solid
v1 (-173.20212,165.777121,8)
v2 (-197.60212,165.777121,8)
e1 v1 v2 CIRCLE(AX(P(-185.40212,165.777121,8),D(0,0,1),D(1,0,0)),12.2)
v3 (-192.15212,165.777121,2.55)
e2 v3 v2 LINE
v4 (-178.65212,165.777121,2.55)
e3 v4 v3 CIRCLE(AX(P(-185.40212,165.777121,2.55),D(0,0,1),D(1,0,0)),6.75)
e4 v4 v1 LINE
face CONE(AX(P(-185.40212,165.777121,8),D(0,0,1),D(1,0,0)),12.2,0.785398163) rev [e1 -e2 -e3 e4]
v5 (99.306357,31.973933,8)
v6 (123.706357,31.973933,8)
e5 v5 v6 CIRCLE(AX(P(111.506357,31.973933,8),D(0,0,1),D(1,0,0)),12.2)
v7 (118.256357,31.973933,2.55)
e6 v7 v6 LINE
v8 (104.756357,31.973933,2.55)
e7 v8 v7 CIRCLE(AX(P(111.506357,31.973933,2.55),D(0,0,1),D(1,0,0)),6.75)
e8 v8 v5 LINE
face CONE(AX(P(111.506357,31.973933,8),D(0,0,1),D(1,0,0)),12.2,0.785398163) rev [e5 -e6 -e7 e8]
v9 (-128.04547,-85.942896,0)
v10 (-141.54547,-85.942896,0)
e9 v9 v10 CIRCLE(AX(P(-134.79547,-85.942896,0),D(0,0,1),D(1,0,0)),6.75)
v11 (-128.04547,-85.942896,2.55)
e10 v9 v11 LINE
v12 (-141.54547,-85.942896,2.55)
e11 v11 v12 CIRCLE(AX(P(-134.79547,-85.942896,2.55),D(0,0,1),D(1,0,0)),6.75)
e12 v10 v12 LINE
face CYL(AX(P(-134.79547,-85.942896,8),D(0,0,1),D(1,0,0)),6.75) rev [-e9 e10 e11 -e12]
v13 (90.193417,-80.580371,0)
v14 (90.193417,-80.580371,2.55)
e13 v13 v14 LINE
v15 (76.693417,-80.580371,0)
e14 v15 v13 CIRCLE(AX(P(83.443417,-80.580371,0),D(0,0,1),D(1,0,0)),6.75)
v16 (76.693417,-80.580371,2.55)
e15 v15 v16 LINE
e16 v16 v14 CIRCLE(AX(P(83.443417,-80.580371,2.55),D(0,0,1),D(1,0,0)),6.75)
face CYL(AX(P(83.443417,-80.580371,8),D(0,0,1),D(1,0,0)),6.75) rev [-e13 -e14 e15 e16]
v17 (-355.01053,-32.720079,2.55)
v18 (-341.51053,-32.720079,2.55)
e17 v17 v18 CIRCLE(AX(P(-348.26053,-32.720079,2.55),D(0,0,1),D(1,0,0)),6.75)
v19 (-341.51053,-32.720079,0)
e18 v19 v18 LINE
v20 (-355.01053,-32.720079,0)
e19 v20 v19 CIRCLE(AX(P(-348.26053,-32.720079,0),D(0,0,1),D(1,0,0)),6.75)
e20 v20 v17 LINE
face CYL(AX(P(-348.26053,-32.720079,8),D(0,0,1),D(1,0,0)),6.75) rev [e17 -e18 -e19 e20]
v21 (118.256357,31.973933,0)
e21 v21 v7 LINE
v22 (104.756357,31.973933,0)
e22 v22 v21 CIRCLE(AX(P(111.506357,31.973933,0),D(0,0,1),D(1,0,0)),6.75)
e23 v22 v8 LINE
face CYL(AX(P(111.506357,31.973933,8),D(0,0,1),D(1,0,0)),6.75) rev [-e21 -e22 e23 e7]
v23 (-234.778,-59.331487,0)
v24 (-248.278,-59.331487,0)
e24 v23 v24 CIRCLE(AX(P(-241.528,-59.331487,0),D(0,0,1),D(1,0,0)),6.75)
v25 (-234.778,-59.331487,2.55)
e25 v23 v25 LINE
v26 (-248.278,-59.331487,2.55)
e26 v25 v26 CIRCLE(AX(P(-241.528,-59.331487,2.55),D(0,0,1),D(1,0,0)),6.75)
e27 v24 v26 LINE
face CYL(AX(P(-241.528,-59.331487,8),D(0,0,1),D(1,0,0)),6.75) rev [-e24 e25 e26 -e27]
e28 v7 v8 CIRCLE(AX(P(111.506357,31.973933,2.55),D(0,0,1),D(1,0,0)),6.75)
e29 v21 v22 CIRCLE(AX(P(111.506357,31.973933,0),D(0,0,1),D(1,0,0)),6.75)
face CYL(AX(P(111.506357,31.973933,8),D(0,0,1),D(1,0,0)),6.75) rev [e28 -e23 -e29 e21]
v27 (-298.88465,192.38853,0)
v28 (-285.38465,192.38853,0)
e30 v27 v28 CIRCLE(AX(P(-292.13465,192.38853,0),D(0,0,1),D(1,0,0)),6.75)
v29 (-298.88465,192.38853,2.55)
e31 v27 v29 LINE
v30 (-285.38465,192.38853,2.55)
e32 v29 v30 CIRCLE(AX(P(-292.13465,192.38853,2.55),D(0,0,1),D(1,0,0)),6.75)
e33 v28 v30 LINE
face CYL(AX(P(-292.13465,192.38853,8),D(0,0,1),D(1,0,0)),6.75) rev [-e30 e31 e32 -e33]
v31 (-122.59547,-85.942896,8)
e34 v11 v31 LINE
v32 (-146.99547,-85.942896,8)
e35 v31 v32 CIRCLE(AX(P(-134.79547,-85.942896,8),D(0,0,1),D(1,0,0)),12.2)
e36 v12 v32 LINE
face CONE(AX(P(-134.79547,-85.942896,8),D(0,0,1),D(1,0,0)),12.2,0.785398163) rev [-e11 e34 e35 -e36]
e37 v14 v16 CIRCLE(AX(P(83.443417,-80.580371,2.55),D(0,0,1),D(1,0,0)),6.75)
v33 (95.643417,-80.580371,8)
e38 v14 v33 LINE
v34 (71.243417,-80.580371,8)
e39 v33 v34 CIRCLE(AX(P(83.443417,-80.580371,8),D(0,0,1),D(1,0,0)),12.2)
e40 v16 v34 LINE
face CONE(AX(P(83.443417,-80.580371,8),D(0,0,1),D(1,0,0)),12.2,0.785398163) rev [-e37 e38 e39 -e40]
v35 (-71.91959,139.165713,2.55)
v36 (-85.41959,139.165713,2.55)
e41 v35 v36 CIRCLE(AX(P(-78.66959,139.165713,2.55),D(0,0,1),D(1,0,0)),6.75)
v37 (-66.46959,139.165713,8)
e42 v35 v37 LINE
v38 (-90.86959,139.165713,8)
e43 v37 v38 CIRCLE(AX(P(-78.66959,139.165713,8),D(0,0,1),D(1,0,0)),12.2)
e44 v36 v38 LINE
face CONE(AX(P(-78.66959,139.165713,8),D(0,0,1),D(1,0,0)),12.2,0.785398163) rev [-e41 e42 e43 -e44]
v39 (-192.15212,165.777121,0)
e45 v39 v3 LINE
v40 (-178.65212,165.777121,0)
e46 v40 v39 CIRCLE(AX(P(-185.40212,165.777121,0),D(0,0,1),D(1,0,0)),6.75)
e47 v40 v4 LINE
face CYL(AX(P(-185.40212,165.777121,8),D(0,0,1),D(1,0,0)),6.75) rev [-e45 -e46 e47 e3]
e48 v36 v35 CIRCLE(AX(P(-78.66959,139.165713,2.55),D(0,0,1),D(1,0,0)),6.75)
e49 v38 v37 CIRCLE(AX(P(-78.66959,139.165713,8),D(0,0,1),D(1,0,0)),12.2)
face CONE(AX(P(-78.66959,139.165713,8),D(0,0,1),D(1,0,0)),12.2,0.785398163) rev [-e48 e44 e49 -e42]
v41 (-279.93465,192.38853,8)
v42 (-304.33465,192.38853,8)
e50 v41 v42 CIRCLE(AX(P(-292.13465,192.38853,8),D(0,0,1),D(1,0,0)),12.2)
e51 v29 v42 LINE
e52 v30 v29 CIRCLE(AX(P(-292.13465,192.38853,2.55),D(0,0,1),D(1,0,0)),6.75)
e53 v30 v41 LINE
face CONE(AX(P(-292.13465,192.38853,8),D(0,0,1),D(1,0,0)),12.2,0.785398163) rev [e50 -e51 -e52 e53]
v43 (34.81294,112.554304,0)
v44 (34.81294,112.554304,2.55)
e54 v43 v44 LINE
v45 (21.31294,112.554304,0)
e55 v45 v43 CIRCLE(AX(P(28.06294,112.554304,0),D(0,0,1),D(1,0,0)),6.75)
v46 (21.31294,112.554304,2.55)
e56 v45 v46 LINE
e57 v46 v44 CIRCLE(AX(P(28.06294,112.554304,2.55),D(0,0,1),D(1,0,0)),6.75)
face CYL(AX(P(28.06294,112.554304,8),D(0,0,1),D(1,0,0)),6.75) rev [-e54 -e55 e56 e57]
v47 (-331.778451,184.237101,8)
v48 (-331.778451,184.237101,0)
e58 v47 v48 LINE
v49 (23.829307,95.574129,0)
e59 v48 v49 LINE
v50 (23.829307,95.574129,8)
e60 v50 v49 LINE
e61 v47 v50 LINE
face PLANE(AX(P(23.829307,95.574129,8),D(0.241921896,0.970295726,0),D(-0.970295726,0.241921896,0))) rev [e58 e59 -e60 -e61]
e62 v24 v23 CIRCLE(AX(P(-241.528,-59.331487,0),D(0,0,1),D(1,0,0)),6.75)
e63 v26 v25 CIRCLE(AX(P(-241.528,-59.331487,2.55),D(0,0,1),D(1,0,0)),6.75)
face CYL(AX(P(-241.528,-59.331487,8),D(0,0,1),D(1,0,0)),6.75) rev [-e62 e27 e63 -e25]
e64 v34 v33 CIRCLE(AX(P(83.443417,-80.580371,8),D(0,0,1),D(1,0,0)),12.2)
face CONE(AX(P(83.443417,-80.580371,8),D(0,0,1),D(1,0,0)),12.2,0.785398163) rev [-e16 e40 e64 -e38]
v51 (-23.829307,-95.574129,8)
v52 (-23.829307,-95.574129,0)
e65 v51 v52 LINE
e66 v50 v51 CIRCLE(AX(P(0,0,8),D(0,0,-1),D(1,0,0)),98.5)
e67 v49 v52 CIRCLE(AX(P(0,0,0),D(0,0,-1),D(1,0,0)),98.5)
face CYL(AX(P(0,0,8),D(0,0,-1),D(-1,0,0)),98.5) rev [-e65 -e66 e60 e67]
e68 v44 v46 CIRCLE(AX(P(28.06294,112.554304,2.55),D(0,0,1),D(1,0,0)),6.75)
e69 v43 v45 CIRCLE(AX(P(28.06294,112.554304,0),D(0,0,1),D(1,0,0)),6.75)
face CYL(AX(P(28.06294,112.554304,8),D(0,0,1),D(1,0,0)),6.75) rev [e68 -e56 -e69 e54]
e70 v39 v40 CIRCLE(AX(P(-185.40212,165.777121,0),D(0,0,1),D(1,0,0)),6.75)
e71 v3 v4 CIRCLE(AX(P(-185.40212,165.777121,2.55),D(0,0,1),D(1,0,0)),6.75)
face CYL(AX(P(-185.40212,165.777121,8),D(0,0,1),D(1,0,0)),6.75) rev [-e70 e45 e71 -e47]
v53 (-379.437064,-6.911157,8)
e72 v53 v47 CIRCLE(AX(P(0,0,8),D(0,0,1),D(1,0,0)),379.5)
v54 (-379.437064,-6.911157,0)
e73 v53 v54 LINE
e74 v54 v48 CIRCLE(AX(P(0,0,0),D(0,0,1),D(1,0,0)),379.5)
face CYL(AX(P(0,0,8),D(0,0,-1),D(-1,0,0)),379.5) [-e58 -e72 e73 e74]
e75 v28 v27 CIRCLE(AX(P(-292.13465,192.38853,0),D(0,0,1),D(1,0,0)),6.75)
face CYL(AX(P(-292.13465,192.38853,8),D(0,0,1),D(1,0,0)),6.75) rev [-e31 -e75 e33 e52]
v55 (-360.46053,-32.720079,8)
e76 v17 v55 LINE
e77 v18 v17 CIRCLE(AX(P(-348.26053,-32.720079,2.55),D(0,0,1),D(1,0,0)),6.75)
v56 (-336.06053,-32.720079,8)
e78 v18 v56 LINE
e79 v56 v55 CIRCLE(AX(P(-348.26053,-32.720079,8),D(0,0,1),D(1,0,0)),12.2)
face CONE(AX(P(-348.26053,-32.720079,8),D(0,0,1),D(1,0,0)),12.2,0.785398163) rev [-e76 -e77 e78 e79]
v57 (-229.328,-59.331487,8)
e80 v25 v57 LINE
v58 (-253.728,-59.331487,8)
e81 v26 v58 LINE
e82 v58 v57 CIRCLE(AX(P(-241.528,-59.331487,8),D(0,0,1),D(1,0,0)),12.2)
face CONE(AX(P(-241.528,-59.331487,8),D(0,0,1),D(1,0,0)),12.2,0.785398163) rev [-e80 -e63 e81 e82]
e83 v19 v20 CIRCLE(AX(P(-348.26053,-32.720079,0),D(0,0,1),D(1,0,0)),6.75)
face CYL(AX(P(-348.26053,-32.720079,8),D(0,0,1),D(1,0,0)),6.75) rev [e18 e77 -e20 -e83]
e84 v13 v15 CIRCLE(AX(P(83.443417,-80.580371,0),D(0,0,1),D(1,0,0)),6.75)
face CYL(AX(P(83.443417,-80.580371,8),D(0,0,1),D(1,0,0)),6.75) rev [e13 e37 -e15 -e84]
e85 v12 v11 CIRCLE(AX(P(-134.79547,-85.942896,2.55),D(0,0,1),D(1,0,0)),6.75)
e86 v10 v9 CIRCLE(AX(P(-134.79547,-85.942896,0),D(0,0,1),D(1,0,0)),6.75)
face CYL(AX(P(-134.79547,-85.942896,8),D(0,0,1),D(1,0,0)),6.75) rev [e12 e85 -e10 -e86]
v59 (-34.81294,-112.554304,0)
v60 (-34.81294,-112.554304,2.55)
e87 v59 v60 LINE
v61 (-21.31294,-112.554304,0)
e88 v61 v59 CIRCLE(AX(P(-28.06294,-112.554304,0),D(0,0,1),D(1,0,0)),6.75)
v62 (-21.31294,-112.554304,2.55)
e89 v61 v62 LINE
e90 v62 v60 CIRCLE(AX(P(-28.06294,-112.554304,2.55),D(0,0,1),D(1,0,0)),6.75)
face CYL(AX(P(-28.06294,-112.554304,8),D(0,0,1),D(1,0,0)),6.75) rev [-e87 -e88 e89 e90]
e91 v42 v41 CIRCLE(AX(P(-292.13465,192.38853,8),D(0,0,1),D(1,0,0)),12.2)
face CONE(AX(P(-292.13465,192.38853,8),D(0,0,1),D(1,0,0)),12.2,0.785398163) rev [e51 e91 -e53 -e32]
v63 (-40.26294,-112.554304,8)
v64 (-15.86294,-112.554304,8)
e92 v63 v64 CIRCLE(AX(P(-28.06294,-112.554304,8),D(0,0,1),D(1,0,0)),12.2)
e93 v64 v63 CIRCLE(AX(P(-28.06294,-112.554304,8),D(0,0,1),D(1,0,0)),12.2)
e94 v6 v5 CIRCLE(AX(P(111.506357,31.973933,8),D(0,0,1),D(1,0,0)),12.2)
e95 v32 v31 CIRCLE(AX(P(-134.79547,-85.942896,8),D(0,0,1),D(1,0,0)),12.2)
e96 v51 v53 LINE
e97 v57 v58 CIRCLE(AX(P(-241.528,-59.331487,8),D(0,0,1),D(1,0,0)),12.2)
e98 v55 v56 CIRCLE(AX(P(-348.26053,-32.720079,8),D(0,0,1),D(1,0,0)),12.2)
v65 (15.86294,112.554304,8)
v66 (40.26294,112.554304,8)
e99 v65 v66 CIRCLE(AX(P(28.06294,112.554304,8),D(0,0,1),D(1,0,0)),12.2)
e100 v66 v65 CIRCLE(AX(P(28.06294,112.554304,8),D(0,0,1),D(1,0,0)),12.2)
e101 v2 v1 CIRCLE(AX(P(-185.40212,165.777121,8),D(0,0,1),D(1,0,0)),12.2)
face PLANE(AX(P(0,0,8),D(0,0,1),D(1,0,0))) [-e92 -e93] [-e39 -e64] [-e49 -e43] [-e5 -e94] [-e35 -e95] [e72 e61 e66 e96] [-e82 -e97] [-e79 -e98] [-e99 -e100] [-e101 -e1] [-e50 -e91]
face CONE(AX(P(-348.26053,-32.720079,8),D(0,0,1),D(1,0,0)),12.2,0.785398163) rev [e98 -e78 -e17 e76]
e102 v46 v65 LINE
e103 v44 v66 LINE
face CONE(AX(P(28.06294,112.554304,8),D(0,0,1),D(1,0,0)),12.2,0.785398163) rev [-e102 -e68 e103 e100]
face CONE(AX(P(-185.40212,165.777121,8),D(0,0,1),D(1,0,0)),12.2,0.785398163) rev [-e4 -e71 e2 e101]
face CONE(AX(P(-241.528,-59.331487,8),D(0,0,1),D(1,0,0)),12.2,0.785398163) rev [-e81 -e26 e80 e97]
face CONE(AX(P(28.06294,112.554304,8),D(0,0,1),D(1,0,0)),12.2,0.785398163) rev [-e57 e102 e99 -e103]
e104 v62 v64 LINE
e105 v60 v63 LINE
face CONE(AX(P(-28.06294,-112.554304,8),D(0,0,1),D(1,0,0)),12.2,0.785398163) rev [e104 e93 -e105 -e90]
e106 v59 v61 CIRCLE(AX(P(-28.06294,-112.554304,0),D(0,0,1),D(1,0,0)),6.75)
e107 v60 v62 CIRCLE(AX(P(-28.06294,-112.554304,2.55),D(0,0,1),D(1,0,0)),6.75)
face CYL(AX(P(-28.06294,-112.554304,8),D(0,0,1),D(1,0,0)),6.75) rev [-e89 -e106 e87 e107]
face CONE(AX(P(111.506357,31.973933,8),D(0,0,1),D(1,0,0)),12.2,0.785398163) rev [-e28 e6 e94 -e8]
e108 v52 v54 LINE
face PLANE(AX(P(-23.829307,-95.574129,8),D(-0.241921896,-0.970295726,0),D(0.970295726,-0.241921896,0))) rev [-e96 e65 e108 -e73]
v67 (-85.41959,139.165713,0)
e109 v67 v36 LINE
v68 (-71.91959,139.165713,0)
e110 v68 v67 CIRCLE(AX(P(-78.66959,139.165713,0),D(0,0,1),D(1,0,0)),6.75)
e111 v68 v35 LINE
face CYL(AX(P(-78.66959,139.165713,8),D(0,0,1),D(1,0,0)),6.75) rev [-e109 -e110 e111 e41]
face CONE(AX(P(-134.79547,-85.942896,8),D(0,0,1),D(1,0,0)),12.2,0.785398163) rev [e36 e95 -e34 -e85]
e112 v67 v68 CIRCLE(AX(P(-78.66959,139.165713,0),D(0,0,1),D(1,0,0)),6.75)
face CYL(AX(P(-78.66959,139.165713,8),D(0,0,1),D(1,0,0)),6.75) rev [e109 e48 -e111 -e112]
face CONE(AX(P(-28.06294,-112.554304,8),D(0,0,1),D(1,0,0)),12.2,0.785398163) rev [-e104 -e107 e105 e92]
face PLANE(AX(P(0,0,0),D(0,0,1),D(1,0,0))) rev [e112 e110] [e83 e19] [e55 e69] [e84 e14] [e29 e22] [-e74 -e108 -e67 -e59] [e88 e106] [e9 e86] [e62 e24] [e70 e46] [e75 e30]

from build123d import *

# Parameters (mm, degrees)
BOSS_EXTRUDE1_DEPTH                        = 8
HOLE_SIZE_PER_FOR_TYPE_1_HEX_SOCK_2_COUNT  = 2
HOLE_SIZE_PER_FOR_TYPE_1_HEX_SOCK_2_PITCH  = 110
HOLE_SIZE_PER_FOR_TYPE_1_HEX_SOCK_3_COUNT  = 2
HOLE_SIZE_PER_FOR_TYPE_1_HEX_SOCK_3_PITCH  = 220
HOLE_SIZE_PER_FOR_TYPE_1_HEX_SOCK_4_COUNT  = 2
HOLE_SIZE_PER_FOR_TYPE_1_HEX_SOCK_4_PITCH  = 330
HOLE_SIZE_PER_FOR_TYPE_1_HEX_SOCK_5_COUNT  = 2
HOLE_SIZE_PER_FOR_TYPE_1_HEX_SOCK_5_PITCH  = 434.348828609
HOLE_SIZE_PER_FOR_TYPE_1_HEX_SOCK_6_COUNT  = 2
HOLE_SIZE_PER_FOR_TYPE_1_HEX_SOCK_6_PITCH  = 464.296139241
HOLE_SIZE_PER_FOR_TYPE_1_HEX_SOCK_7_COUNT  = 2
HOLE_SIZE_PER_FOR_TYPE_1_HEX_SOCK_7_PITCH  = 403.390629539
HOLE_SIZE_PER_FOR_TYPE_1_HEX_SOCK_8_COUNT  = 2
HOLE_SIZE_PER_FOR_TYPE_1_HEX_SOCK_8_PITCH  = 319.724881734
HOLE_SIZE_PER_FOR_TYPE_1_HEX_SOCK_9_COUNT  = 2
HOLE_SIZE_PER_FOR_TYPE_1_HEX_SOCK_9_PITCH  = 256.756694168
HOLE_SIZE_PER_FOR_TYPE_1_HEX_SOCK_10_COUNT = 2
HOLE_SIZE_PER_FOR_TYPE_1_HEX_SOCK_10_PITCH = 232


with BuildPart() as part:
    # Sketch1 → Boss-Extrude1 (new body)
    with BuildSketch(Plane.XY):
        with BuildLine():
            Line((23.829306717, 95.574129038), (-331.778451057, 184.237101079))
            ThreePointArc((-331.778451057, 184.237101079), (368.227228122, -91.80935938), (-379.43706449, -6.911156997))
            Line((-379.43706449, -6.911156997), (-23.829306717, -95.574129038))
            ThreePointArc((-23.829306717, -95.574129038), (95.574129038, -23.829306717), (23.829306717, 95.574129038))
        make_face()
    extrude(amount=BOSS_EXTRUDE1_DEPTH)

    # Sketch6 → Hole size (per %) for Type 1 hex socket Torx semi-countersunk screw (revolve, cut)
    with BuildSketch(Plane(origin=(-292.134649782, 192.388529796, 8), x_dir=(0, -1, 0), z_dir=(1, 0, 0))):
        Polygon((0, 0), (0, 8), (6.75, 8), (6.75, 5.45), (12.2, 0), align=None)
    hole_size_per_for_type_1_hex_socket_t = revolve(axis=Axis((-292.134649782, 192.388529796, 14.35), (0, 0, -1)), mode=Mode.SUBTRACT)

    # Hole size _per _ for Type 1 hex sock 2: Hole size (per %) for Type 1 hex socket Torx semi-countersunk screw ×2
    with Locations(*[Vector(0.9702957262760132, -0.24192189559960064, 0) * (i * HOLE_SIZE_PER_FOR_TYPE_1_HEX_SOCK_2_PITCH) for i in range(1, HOLE_SIZE_PER_FOR_TYPE_1_HEX_SOCK_2_COUNT)]):
        add(hole_size_per_for_type_1_hex_socket_t, mode=Mode.SUBTRACT)

    # Hole size _per _ for Type 1 hex sock 3: Hole size (per %) for Type 1 hex socket Torx semi-countersunk screw ×2
    with Locations(*[Vector(0.9702957262760132, -0.24192189559960078, 0) * (i * HOLE_SIZE_PER_FOR_TYPE_1_HEX_SOCK_3_PITCH) for i in range(1, HOLE_SIZE_PER_FOR_TYPE_1_HEX_SOCK_3_COUNT)]):
        add(hole_size_per_for_type_1_hex_socket_t, mode=Mode.SUBTRACT)

    # Hole size _per _ for Type 1 hex sock 4: Hole size (per %) for Type 1 hex socket Torx semi-countersunk screw ×2
    with Locations(*[Vector(0.9702957262760132, -0.24192189559960064, 0) * (i * HOLE_SIZE_PER_FOR_TYPE_1_HEX_SOCK_4_PITCH) for i in range(1, HOLE_SIZE_PER_FOR_TYPE_1_HEX_SOCK_4_COUNT)]):
        add(hole_size_per_for_type_1_hex_socket_t, mode=Mode.SUBTRACT)

    # Hole size _per _ for Type 1 hex sock 5: Hole size (per %) for Type 1 hex socket Torx semi-countersunk screw ×2
    with Locations(*[Vector(0.9293014736642066, -0.36932204245825073, 0) * (i * HOLE_SIZE_PER_FOR_TYPE_1_HEX_SOCK_5_PITCH) for i in range(1, HOLE_SIZE_PER_FOR_TYPE_1_HEX_SOCK_5_COUNT)]):
        add(hole_size_per_for_type_1_hex_socket_t, mode=Mode.SUBTRACT)

    # Hole size _per _ for Type 1 hex sock 6: Hole size (per %) for Type 1 hex socket Torx semi-countersunk screw ×2
    with Locations(*[Vector(0.8089192109912862, -0.587919816037217, 0) * (i * HOLE_SIZE_PER_FOR_TYPE_1_HEX_SOCK_6_PITCH) for i in range(1, HOLE_SIZE_PER_FOR_TYPE_1_HEX_SOCK_6_COUNT)]):
        add(hole_size_per_for_type_1_hex_socket_t, mode=Mode.SUBTRACT)

    # Hole size _per _ for Type 1 hex sock 7: Hole size (per %) for Type 1 hex socket Torx semi-countersunk screw ×2
    with Locations(*[Vector(0.6546302530469048, -0.7559492256730906, 0) * (i * HOLE_SIZE_PER_FOR_TYPE_1_HEX_SOCK_7_PITCH) for i in range(1, HOLE_SIZE_PER_FOR_TYPE_1_HEX_SOCK_7_COUNT)]):
        add(hole_size_per_for_type_1_hex_socket_t, mode=Mode.SUBTRACT)

    # Hole size _per _ for Type 1 hex sock 8: Hole size (per %) for Type 1 hex socket Torx semi-countersunk screw ×2
    with Locations(*[Vector(0.49210802471224957, -0.8705341417852651, 0) * (i * HOLE_SIZE_PER_FOR_TYPE_1_HEX_SOCK_8_PITCH) for i in range(1, HOLE_SIZE_PER_FOR_TYPE_1_HEX_SOCK_8_COUNT)]):
        add(hole_size_per_for_type_1_hex_socket_t, mode=Mode.SUBTRACT)

    # Hole size _per _ for Type 1 hex sock 9: Hole size (per %) for Type 1 hex socket Torx semi-countersunk screw ×2
    with Locations(*[Vector(0.19709963269028047, -0.9803834631374382, 0) * (i * HOLE_SIZE_PER_FOR_TYPE_1_HEX_SOCK_9_PITCH) for i in range(1, HOLE_SIZE_PER_FOR_TYPE_1_HEX_SOCK_9_COUNT)]):
        add(hole_size_per_for_type_1_hex_socket_t, mode=Mode.SUBTRACT)

    # Hole size _per _ for Type 1 hex sock 10: Hole size (per %) for Type 1 hex socket Torx semi-countersunk screw ×2
    with Locations(*[Vector(-0.24192189559966096, -0.9702957262759981, 0) * (i * HOLE_SIZE_PER_FOR_TYPE_1_HEX_SOCK_10_PITCH) for i in range(1, HOLE_SIZE_PER_FOR_TYPE_1_HEX_SOCK_10_COUNT)]):
        add(hole_size_per_for_type_1_hex_socket_t, mode=Mode.SUBTRACT)


solid = part.part
